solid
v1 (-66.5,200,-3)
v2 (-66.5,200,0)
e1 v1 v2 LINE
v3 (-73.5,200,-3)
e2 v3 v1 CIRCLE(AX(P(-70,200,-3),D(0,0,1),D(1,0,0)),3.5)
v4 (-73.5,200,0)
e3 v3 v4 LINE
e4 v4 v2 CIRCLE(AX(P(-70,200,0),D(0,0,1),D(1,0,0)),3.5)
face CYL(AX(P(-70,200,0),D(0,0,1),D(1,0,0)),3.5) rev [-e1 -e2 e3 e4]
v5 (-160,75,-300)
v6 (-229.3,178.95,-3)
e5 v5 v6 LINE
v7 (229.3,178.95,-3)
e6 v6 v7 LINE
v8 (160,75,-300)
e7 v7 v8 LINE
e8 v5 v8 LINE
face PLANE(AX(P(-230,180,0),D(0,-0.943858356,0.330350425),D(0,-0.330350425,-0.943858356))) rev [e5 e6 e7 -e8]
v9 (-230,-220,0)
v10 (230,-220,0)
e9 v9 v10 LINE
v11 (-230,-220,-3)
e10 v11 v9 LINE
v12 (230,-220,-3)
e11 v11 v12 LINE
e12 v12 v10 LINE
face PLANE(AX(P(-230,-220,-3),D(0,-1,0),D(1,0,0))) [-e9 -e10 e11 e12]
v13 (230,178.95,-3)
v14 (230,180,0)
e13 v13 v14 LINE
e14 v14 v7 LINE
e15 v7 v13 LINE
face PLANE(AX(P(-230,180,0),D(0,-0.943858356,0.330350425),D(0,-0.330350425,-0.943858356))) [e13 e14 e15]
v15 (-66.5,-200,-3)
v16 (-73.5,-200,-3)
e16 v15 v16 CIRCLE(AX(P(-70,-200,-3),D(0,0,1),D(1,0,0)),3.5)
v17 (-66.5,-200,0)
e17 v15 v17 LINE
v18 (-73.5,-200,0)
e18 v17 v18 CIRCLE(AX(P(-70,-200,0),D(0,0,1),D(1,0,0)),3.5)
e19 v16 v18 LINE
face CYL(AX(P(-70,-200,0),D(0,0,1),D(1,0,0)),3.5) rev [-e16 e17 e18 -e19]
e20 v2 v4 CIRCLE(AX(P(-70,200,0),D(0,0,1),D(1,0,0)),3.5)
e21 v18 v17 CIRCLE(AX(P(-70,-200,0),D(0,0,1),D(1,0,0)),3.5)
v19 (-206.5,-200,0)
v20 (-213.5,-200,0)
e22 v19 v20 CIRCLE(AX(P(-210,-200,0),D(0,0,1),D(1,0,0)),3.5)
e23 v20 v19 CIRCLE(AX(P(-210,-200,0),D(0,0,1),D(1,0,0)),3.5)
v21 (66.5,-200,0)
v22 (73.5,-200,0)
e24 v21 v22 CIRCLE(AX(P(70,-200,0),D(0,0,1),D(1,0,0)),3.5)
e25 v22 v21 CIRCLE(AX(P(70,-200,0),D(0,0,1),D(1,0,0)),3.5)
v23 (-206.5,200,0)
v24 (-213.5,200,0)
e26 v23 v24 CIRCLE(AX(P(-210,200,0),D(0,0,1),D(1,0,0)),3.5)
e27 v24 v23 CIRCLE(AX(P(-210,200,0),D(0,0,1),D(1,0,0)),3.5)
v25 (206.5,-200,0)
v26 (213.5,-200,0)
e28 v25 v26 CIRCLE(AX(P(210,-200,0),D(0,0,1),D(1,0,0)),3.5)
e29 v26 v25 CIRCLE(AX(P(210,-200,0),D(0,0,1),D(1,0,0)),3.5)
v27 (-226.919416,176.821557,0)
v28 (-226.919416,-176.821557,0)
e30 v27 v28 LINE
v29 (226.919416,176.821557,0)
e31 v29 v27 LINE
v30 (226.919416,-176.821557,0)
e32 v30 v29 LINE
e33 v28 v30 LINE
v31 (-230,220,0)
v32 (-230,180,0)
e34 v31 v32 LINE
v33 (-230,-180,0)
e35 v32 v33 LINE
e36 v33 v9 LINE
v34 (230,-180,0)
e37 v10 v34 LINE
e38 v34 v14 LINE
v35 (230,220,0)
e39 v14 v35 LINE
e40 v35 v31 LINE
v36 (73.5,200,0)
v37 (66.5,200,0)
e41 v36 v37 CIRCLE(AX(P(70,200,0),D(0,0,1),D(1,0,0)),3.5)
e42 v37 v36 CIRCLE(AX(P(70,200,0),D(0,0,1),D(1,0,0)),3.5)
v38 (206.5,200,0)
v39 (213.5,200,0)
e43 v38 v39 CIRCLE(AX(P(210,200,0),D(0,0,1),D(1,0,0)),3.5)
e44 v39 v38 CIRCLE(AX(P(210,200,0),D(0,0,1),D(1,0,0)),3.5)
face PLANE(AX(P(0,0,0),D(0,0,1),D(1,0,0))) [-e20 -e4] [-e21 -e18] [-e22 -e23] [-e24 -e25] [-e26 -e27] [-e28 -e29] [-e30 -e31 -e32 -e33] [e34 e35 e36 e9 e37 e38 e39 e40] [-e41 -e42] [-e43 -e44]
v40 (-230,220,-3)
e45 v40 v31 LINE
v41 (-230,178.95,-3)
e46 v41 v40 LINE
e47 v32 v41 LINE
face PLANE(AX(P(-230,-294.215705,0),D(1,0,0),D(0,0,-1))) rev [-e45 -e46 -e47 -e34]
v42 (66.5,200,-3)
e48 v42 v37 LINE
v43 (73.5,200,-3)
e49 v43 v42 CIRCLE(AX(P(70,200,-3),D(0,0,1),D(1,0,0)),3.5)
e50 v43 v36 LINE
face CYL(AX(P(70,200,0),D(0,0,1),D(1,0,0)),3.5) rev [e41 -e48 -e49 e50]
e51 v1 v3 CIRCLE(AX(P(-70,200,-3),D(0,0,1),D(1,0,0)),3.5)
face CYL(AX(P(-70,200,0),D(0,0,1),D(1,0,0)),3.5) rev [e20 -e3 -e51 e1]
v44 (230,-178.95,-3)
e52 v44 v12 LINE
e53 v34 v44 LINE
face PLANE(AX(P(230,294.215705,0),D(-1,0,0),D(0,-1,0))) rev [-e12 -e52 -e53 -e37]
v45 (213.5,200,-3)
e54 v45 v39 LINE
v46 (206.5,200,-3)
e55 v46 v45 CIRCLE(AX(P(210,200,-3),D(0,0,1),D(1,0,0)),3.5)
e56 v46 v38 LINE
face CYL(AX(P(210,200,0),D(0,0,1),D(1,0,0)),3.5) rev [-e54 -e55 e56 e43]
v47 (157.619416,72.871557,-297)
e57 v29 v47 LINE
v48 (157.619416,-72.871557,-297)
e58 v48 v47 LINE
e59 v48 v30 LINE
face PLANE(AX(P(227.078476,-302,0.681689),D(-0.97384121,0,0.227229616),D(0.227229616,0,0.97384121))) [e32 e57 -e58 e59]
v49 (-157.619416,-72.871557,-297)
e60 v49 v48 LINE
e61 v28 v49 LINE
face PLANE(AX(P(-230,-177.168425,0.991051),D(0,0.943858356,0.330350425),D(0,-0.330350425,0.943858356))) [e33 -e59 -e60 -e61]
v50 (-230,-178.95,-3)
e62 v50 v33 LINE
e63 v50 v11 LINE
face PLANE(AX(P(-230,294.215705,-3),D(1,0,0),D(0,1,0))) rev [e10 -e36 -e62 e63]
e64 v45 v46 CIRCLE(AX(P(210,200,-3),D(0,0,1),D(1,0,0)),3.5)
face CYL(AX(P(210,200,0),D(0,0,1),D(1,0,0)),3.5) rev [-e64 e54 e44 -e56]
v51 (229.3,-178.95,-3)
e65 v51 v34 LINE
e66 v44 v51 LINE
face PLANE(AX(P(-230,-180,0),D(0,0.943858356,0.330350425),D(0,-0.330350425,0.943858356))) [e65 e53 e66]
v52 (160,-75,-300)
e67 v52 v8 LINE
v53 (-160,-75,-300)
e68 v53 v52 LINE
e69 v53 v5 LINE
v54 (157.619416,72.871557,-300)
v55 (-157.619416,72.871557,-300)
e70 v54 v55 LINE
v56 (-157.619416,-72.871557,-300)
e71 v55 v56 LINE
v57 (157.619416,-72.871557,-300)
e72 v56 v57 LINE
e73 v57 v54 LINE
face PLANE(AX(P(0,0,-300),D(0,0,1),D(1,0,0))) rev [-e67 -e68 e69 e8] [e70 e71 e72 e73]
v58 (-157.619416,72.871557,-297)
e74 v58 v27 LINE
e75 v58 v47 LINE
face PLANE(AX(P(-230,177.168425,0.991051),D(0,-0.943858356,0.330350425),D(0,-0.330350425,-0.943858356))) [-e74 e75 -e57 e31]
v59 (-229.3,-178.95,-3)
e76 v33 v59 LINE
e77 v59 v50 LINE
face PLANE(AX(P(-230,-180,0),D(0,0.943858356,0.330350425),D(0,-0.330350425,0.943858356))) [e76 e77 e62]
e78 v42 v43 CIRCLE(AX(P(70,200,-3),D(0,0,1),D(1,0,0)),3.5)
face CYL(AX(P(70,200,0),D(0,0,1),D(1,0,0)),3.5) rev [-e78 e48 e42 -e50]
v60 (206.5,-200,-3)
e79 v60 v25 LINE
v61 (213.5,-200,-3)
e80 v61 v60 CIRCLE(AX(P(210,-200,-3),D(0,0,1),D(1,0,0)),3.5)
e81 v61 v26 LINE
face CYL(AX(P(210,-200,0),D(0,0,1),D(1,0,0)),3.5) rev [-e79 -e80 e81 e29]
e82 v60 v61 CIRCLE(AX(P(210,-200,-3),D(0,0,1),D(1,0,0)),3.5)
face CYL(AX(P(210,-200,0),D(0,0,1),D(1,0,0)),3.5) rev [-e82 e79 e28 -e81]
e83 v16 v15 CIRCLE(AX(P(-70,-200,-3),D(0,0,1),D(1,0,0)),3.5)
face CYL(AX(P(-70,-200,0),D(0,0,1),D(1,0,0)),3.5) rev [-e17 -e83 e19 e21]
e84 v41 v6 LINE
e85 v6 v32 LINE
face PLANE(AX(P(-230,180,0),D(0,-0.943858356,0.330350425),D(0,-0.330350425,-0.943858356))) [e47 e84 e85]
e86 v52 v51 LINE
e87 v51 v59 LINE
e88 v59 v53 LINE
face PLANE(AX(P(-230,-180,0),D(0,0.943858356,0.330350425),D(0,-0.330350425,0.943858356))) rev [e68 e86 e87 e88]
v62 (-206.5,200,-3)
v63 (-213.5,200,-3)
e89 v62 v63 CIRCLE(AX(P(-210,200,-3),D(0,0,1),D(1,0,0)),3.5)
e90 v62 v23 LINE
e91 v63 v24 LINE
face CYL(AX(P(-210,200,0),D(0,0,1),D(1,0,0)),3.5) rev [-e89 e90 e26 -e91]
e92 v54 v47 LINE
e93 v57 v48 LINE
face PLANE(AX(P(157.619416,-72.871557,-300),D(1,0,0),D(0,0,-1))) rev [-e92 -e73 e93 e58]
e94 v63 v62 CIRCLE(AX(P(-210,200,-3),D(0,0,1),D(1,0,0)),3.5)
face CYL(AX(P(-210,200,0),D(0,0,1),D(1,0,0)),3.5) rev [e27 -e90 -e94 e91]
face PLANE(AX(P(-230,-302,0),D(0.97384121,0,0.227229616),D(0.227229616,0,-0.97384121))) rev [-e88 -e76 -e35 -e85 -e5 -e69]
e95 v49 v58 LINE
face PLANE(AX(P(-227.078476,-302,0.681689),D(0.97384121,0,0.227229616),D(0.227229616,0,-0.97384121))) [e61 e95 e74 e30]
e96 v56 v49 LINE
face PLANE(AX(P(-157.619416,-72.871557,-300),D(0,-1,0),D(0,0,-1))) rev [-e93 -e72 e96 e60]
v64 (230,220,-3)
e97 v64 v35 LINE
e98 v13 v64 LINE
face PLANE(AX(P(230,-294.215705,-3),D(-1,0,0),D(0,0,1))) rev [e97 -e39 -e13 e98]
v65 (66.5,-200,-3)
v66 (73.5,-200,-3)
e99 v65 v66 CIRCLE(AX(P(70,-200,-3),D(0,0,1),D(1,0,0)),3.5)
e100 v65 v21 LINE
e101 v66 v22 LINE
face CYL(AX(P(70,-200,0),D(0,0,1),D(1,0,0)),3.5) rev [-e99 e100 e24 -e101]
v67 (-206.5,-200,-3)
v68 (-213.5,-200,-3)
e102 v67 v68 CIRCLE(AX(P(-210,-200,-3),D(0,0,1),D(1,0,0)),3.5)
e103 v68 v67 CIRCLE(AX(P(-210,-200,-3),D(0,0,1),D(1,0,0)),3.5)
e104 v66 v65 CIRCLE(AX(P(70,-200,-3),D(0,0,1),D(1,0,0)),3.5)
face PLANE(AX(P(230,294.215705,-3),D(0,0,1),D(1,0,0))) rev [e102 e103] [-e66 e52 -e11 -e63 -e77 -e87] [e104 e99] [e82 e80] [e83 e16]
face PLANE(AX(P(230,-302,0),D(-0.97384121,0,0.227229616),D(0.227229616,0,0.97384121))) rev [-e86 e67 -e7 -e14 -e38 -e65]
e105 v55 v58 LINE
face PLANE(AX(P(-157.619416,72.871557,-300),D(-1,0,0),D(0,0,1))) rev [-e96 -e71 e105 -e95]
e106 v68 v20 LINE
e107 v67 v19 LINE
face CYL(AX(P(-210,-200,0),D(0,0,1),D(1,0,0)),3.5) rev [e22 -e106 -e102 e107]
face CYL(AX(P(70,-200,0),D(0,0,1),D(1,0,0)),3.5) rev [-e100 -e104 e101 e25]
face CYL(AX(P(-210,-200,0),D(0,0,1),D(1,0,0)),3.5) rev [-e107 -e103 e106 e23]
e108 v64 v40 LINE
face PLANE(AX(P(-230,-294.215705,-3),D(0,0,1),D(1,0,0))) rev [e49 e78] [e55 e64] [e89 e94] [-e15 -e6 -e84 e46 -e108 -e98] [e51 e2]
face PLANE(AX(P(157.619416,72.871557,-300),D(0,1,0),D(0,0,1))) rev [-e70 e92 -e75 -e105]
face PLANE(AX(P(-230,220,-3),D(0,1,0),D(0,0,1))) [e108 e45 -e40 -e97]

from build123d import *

# Parameters (mm, degrees)
SKETCH1_W                = 460
SKETCH1_H                = 360
BOSS_EXTRUDE1_DEPTH      = 300
CUT_EXTRUDE1_DEPTH       = 578.927331072
CUT_EXTRUDE3_DEPTH       = 302
SHELL1_T                 = -3
SKETCH7_W                = 315.23883128
SKETCH7_H                = 145.74311397
CUT_EXTRUDE4_DEPTH       = 417.544115311
SKETCH8_W                = 460
SKETCH8_H                = 40
BOSS_EXTRUDE2_DEPTH      = 3
BOSS_EXTRUDE3_REACH      = 524.015
SKETCH9_W                = 460
SKETCH9_H                = 3
SKETCH10_W               = 460
SKETCH10_H               = 40
BOSS_EXTRUDE4_DEPTH      = 3
BOSS_EXTRUDE5_REACH      = 552.364
SKETCH11_W               = 460
SKETCH11_H               = 3
F_7_0_7_DIAMETER_HOLE1_D = 7
LPATTERN1_COUNT          = 4
LPATTERN1_PITCH          = 140
MIRROR5_COPY_1_D         = 7
MIRROR5_COPY_2_D         = 7
MIRROR5_COPY_3_D         = 7


with BuildPart() as part:
    # Sketch1 → Boss-Extrude1 (new body)
    with BuildSketch(Plane.XY):
        Rectangle(SKETCH1_W, SKETCH1_H)
    extrude(amount=-BOSS_EXTRUDE1_DEPTH)

    # Sketch3 → Cut-Extrude1 (cut, through all)
    with BuildSketch(Plane(origin=(230, 0, 0), x_dir=(0, 0, -1), z_dir=(1, 0, 0))):
        Polygon((0, 180), (300, 75), (300, 180), align=None)
        Polygon((300, -180), (0, -180), (300, -75), align=None)
    extrude(amount=-CUT_EXTRUDE1_DEPTH, mode=Mode.SUBTRACT)

    # Sketch6 → Cut-Extrude3 (cut, symmetric)
    with BuildSketch(Plane(origin=(0, 0, 0), x_dir=(1, 0, 0), z_dir=(0, 1, 0))):
        Polygon((-230, 0), (-160, 300), (-230, 300), align=None)
        Polygon((230, 300), (230, 0), (160, 300), align=None)
    extrude(amount=CUT_EXTRUDE3_DEPTH, both=True, mode=Mode.SUBTRACT)

    # Shell1
    shell1_openings = [part.faces().sort_by_distance(p)[0] for p in [
        (0, 0, 0),
    ]]
    offset(amount=SHELL1_T, openings=shell1_openings, kind=Kind.INTERSECTION)

    # Sketch7 → Cut-Extrude4 (cut, through all)
    with BuildSketch(Plane.XY.offset(-297)):
        Rectangle(SKETCH7_W, SKETCH7_H)
    extrude(amount=-CUT_EXTRUDE4_DEPTH, mode=Mode.SUBTRACT)

    # Boss-Extrude3: up to this face of the body (flat: up to its plane)
    boss_extrude3_end = Plane(part.part.faces().sort_by_distance((0, -130.641025641, -141.025641026))[0])
    # Sketch9 → Boss-Extrude3 (add, up to the picked face)
    with BuildSketch(Plane(origin=(0, -180, 0), x_dir=(1, 0, 0), z_dir=(0, 1, 0)), mode=Mode.PRIVATE) as boss_extrude3_sk1:
        with Locations((0, 1.5)):
            Rectangle(SKETCH9_W, SKETCH9_H)
    boss_extrude3_tool1 = split(extrude(boss_extrude3_sk1.sketch, amount=BOSS_EXTRUDE3_REACH, mode=Mode.PRIVATE), bisect_by=boss_extrude3_end, keep=Keep.BOTH, mode=Mode.PRIVATE)


with BuildPart() as body_2:
    # Sketch8 → Boss-Extrude2 (new body)
    with BuildSketch(Plane.XY):
        with Locations((0, -200)):
            Rectangle(SKETCH8_W, SKETCH8_H)
    extrude(amount=-BOSS_EXTRUDE2_DEPTH)


with BuildPart() as part_1:
    add(part.part)

    add(body_2.part)  # Boss-Extrude3 merges body 2
    add(boss_extrude3_tool1.solids().sort_by(Axis((0, -180, -1.5), (0, 1, 0)))[0])

    # Boss-Extrude5: up to this face of the body (flat: up to its plane)
    boss_extrude5_end = Plane(part_1.part.faces().sort_by_distance((0, 130.641025641, -141.025641026))[0])
    # Sketch11 → Boss-Extrude5 (add, up to the picked face)
    with BuildSketch(Plane.XZ.offset(-180), mode=Mode.PRIVATE) as boss_extrude5_sk1:
        with Locations((0, -1.5)):
            Rectangle(SKETCH11_W, SKETCH11_H)
    boss_extrude5_tool1 = split(extrude(boss_extrude5_sk1.sketch, amount=BOSS_EXTRUDE5_REACH, mode=Mode.PRIVATE), bisect_by=boss_extrude5_end, keep=Keep.BOTH, mode=Mode.PRIVATE)


with BuildPart() as body_2_2:
    # Sketch10 → Boss-Extrude4 (new body)
    with BuildSketch(Plane.XY):
        with Locations((0, 200)):
            Rectangle(SKETCH10_W, SKETCH10_H)
    extrude(amount=-BOSS_EXTRUDE4_DEPTH)


with BuildPart() as part_2:
    add(part_1.part)

    add(body_2_2.part)  # Boss-Extrude5 merges body 2 2
    add(boss_extrude5_tool1.solids().sort_by(Axis((0, 180, -1.5), (0, -1, 0)))[0])

    # Ø7.0 (7) Diameter Hole1 (through all)
    with Locations(Plane.XY):
        with Locations((-210, 200)):
            f_7_0_7_diameter_hole1 = Hole(F_7_0_7_DIAMETER_HOLE1_D / 2)

    # LPattern1: Ø7.0 (7) Diameter Hole1 ×4
    with Locations(*[(i * LPATTERN1_PITCH, 0, 0) for i in range(1, LPATTERN1_COUNT)]):
        add(f_7_0_7_diameter_hole1, mode=Mode.SUBTRACT)

    # Mirror5: Ø7.0 (7) Diameter Hole1 across plane
    add(f_7_0_7_diameter_hole1.mirror(Plane.ZX), mode=Mode.SUBTRACT)

    # Mirror5 copy 1 (through all)
    with Locations(Plane(origin=(140, 0, 0), x_dir=(1, 0, 0), z_dir=(0, 0, 1))):
        with Locations((-210, -200)):
            Hole(MIRROR5_COPY_1_D / 2)

    # Mirror5 copy 2 (through all)
    with Locations(Plane(origin=(280, 0, 0), x_dir=(1, 0, 0), z_dir=(0, 0, 1))):
        with Locations((-210, -200)):
            Hole(MIRROR5_COPY_2_D / 2)

    # Mirror5 copy 3 (through all)
    with Locations(Plane(origin=(420, 0, 0), x_dir=(1, 0, 0), z_dir=(0, 0, 1))):
        with Locations((-210, -200)):
            Hole(MIRROR5_COPY_3_D / 2)


solid = part_2.part
